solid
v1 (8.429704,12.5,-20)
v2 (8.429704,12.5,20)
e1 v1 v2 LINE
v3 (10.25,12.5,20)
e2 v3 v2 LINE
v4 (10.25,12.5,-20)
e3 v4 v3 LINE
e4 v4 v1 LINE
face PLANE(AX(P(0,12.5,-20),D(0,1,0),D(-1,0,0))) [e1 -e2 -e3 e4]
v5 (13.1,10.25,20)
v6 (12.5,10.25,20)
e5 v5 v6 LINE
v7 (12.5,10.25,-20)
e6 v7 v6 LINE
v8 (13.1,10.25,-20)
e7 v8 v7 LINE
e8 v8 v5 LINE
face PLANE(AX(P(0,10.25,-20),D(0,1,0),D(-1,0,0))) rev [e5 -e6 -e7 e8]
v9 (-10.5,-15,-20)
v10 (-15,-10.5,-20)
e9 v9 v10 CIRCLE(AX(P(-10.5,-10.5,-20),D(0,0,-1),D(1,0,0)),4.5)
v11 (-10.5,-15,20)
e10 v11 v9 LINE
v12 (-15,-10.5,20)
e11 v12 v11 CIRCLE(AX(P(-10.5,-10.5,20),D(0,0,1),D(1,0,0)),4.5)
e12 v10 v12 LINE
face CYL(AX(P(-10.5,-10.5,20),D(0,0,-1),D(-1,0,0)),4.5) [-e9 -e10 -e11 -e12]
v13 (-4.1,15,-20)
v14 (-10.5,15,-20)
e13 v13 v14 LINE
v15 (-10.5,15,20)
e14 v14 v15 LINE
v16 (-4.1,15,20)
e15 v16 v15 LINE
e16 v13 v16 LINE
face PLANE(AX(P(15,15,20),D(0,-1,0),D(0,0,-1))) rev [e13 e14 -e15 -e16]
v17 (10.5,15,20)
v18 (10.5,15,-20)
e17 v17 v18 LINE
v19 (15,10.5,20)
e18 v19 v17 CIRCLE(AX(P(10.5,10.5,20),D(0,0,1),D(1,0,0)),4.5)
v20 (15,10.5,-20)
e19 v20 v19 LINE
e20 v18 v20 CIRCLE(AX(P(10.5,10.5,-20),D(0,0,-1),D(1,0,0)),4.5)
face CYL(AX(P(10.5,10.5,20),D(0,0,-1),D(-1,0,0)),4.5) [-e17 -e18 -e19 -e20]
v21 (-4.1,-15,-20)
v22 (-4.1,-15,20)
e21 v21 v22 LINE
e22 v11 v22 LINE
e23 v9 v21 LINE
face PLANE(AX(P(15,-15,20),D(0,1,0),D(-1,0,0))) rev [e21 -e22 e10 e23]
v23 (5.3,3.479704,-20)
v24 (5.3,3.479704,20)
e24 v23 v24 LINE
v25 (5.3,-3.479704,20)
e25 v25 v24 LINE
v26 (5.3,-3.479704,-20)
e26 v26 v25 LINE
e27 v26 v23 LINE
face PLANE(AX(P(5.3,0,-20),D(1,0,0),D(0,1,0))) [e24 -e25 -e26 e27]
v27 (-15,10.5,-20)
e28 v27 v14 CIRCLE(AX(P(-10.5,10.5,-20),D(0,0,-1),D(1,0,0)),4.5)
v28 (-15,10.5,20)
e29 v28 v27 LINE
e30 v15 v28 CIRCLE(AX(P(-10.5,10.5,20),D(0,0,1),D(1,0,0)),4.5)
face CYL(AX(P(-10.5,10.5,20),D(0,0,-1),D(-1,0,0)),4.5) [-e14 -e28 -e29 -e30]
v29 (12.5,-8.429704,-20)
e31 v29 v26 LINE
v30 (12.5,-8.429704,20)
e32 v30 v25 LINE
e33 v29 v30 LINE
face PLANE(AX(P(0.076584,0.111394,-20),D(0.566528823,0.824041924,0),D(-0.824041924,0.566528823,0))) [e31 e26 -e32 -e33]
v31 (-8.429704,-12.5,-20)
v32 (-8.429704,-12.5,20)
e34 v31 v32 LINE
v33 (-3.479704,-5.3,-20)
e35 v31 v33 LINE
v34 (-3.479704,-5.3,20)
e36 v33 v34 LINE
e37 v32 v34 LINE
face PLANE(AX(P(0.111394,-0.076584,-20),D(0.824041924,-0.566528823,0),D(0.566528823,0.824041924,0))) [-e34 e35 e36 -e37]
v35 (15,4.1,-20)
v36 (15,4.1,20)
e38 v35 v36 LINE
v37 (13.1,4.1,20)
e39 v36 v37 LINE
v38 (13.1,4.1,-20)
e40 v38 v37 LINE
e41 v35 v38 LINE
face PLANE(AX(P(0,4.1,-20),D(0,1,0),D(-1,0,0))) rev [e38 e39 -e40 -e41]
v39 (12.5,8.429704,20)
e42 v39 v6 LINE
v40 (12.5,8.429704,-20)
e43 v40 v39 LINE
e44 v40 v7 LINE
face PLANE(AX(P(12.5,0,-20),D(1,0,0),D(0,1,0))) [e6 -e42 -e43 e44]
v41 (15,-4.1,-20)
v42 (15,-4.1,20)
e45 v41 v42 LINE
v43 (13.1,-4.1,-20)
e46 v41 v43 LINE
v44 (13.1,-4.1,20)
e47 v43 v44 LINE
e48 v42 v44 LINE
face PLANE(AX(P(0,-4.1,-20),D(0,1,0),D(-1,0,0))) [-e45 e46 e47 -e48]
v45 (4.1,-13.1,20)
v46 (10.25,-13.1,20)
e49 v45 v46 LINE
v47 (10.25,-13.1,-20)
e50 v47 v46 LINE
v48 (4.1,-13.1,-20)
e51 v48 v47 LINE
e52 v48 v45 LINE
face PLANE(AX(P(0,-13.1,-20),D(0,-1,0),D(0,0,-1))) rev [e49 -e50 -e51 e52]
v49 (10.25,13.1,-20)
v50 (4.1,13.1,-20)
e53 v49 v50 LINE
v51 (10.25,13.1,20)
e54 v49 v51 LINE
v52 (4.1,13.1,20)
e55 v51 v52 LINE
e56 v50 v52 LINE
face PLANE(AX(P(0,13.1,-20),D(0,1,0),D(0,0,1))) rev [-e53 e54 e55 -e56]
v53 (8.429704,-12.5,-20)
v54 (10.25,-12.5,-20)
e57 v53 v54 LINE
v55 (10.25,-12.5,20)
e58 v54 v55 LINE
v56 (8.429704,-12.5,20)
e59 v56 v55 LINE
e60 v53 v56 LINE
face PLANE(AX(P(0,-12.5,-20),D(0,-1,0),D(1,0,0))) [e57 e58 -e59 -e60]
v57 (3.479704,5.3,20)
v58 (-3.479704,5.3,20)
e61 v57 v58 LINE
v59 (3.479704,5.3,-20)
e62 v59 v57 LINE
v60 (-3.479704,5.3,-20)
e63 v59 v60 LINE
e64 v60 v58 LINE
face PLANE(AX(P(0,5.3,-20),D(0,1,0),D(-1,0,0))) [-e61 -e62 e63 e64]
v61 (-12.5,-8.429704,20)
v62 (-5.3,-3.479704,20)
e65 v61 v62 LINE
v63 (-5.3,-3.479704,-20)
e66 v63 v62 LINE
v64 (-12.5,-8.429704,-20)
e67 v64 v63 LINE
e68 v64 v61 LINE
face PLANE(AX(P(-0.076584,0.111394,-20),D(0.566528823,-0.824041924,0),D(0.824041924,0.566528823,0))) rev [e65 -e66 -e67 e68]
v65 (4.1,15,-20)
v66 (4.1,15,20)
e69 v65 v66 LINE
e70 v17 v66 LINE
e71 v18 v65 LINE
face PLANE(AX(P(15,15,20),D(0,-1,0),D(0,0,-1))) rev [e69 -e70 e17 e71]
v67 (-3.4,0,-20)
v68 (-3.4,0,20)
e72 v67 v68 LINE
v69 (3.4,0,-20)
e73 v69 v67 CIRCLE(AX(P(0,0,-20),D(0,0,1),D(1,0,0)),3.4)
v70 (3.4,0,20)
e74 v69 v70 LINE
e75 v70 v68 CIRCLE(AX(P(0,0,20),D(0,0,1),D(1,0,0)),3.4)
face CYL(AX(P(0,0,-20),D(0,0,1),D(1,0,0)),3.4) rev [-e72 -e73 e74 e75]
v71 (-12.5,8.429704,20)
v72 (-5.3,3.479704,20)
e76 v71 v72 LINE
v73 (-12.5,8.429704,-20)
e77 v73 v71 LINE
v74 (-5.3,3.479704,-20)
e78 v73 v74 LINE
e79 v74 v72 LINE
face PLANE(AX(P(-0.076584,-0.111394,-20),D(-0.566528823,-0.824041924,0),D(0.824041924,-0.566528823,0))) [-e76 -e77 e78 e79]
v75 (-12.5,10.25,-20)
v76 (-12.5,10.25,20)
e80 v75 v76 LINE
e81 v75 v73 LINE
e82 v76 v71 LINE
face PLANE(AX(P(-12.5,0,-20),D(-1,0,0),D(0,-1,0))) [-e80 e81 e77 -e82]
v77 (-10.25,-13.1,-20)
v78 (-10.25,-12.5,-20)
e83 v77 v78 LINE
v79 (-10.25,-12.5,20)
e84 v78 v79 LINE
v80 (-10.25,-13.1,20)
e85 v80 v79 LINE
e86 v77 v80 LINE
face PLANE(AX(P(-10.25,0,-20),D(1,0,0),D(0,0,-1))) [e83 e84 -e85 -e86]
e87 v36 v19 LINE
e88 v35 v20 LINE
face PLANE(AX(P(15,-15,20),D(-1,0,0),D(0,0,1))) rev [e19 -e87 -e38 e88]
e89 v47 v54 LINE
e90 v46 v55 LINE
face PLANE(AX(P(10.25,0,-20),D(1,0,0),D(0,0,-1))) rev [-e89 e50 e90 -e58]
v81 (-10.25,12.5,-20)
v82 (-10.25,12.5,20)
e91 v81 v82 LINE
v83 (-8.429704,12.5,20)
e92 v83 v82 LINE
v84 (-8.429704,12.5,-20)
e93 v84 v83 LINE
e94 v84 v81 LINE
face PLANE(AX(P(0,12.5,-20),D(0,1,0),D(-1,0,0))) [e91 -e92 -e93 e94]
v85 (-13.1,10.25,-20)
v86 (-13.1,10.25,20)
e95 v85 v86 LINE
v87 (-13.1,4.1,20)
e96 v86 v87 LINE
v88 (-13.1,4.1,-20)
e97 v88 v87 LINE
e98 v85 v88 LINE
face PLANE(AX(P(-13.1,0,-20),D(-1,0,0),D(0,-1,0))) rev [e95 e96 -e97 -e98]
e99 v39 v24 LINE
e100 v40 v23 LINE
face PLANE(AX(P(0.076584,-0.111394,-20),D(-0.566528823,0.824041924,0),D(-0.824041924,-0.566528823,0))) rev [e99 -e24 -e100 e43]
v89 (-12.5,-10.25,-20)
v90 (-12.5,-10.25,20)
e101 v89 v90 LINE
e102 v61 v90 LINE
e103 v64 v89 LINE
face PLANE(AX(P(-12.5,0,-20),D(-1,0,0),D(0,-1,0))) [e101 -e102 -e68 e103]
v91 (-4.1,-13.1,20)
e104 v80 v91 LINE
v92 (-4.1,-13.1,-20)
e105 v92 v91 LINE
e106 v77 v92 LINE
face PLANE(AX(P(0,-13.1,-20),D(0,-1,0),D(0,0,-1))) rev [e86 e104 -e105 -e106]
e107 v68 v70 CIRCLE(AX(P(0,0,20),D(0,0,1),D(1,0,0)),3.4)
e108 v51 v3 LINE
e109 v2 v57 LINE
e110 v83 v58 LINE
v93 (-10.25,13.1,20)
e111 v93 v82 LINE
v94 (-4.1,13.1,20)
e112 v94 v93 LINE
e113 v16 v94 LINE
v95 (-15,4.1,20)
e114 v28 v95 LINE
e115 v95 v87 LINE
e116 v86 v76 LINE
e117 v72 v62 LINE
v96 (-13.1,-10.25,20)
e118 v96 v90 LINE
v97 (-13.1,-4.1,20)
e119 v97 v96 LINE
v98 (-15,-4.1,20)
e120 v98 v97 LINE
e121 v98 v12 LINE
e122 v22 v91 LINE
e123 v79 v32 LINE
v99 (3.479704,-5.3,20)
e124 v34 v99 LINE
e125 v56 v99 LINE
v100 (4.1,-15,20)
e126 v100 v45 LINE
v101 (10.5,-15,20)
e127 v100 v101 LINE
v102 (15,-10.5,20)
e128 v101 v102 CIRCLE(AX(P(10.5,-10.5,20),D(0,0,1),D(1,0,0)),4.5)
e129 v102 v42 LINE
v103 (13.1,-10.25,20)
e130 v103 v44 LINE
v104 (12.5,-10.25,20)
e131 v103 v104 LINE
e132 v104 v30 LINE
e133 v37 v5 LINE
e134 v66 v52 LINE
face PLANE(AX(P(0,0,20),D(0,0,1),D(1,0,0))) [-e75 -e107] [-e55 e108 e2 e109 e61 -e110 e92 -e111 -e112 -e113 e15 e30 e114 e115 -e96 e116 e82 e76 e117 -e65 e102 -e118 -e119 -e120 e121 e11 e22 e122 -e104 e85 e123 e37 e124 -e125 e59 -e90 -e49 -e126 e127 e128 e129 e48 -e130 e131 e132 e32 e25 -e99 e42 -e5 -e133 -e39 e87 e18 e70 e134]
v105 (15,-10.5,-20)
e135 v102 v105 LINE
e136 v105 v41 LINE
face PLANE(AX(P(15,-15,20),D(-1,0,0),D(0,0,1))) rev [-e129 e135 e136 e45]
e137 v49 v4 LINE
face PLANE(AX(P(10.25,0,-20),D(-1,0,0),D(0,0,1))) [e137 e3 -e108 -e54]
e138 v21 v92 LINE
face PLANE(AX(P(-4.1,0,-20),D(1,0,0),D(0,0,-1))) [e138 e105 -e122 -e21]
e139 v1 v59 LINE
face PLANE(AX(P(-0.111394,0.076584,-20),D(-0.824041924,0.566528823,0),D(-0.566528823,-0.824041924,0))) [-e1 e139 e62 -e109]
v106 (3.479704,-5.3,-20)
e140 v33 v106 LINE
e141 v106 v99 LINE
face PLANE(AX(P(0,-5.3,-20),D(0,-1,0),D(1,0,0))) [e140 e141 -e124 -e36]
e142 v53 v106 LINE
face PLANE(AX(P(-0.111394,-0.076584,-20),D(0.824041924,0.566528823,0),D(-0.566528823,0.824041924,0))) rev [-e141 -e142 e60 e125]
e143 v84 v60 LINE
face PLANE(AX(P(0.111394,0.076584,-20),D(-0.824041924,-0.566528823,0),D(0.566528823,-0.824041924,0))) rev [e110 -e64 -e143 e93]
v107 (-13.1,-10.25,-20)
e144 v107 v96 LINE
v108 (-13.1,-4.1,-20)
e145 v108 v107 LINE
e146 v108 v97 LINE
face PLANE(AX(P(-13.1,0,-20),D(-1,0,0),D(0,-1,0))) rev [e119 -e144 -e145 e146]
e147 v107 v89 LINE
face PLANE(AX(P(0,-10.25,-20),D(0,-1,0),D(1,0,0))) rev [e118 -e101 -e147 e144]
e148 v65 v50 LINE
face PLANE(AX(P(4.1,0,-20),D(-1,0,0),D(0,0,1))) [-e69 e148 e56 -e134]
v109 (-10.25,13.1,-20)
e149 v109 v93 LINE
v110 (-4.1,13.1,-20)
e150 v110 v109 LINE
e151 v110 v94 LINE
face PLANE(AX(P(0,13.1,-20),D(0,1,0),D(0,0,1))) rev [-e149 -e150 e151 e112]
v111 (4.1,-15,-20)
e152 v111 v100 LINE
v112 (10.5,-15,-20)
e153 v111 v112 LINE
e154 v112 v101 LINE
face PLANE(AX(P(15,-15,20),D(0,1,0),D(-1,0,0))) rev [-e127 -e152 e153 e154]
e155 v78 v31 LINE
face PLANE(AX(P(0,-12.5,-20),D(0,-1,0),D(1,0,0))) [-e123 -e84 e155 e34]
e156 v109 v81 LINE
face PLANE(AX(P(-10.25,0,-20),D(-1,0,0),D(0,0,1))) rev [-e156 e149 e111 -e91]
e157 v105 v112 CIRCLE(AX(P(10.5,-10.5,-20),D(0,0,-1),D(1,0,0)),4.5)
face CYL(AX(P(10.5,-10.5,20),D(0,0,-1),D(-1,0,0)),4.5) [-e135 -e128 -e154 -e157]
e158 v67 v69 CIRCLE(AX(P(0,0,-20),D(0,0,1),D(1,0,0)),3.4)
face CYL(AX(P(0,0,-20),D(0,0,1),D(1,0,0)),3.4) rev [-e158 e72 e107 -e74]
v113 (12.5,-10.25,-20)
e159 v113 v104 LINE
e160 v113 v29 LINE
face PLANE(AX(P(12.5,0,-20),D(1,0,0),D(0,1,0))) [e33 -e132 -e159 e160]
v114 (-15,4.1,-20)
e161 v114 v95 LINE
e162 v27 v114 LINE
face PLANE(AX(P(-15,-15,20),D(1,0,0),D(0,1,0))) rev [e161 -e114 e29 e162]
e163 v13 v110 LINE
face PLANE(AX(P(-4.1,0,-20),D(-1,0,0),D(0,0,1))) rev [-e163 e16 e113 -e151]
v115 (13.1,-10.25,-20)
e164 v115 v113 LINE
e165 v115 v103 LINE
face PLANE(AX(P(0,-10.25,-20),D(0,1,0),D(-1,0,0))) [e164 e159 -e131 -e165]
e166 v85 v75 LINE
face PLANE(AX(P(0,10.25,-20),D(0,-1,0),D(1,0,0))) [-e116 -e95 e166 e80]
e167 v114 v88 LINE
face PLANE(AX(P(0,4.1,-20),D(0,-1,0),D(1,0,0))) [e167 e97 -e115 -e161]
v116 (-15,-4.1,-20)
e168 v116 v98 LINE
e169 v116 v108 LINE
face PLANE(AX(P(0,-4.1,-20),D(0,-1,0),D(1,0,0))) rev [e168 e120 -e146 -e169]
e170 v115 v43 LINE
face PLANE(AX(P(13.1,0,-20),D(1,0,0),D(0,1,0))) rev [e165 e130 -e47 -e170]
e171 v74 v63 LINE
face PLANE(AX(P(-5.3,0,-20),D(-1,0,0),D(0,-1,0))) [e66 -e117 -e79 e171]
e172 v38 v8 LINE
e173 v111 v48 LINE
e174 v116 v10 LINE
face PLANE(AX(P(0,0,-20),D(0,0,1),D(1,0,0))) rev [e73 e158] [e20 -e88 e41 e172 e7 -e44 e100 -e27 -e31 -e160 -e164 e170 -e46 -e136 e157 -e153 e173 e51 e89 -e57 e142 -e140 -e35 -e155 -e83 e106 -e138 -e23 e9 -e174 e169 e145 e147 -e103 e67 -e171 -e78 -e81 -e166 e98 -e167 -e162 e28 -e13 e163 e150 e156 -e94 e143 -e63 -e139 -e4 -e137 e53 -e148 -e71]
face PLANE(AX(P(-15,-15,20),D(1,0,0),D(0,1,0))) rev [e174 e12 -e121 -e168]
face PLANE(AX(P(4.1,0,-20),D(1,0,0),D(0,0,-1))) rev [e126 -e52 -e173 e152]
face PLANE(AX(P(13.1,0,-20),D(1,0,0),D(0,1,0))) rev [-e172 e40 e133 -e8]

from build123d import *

# Parameters (mm, degrees)
SKETCH_1_W               = 30
SKETCH_1_H               = 30
EXTRUDE_1_DEPTH          = 20
FILLET_1_R               = 4.5
SKETCH_2_W               = 8.2
SKETCH_2_H               = 0.3
SKETCH_2_H_2             = 1.9
SKETCH_2_R               = 3.4
CUT_EXTRUDE_1_DEPTH      = 46.276925691
PATTERN_CIRCULAR_1_COUNT = 4


with BuildPart() as part:
    # 草图1 → 凸台-拉伸1 (new, symmetric)
    with BuildSketch(Plane.XY):
        Rectangle(SKETCH_1_W, SKETCH_1_H)
    extrude(amount=EXTRUDE_1_DEPTH, both=True)

    # 圆角1
    fillet_1_edges = [part.edges().sort_by_distance(p)[0] for p in [
        (-15, 15, 0),
        (15, 15, 0),
        (15, -15, 0),
        (-15, -15, 0),
    ]]
    fillet(fillet_1_edges, radius=FILLET_1_R)

    # 草图2 → 切除-拉伸1 (cut, through all)
    with BuildSketch(Plane.XY.offset(20)):
        with Locations((0, 12.95)):
            Rectangle(SKETCH_2_W, SKETCH_2_H)
        with Locations((0, 14.05)):
            Rectangle(SKETCH_2_W, SKETCH_2_H_2)
        Polygon((10.25, 13.1), (4.1, 13.1), (4.1, 12.8), (-4.1, 12.8), (-4.1, 13.1), (-10.25, 13.1), (-10.25, 12.5), (-8.429704265, 12.5), (8.429704265, 12.5), (10.25, 12.5), align=None)
        Polygon((3.479704265, 5.3), (8.429704265, 12.5), (-8.429704265, 12.5), (-3.479704265, 5.3), align=None)
        Circle(SKETCH_2_R)
    cut_extrude_1 = extrude(amount=-CUT_EXTRUDE_1_DEPTH, mode=Mode.SUBTRACT)

    # 阵列(圆周)1: 切除-拉伸1 ×4 about axis
    pattern_circular_1_axis = Axis((0, 0, 0), (0, 0, 1))
    for i in range(1, PATTERN_CIRCULAR_1_COUNT):
        add(cut_extrude_1.rotate(pattern_circular_1_axis, i * 360 / PATTERN_CIRCULAR_1_COUNT), mode=Mode.SUBTRACT)


solid = part.part
